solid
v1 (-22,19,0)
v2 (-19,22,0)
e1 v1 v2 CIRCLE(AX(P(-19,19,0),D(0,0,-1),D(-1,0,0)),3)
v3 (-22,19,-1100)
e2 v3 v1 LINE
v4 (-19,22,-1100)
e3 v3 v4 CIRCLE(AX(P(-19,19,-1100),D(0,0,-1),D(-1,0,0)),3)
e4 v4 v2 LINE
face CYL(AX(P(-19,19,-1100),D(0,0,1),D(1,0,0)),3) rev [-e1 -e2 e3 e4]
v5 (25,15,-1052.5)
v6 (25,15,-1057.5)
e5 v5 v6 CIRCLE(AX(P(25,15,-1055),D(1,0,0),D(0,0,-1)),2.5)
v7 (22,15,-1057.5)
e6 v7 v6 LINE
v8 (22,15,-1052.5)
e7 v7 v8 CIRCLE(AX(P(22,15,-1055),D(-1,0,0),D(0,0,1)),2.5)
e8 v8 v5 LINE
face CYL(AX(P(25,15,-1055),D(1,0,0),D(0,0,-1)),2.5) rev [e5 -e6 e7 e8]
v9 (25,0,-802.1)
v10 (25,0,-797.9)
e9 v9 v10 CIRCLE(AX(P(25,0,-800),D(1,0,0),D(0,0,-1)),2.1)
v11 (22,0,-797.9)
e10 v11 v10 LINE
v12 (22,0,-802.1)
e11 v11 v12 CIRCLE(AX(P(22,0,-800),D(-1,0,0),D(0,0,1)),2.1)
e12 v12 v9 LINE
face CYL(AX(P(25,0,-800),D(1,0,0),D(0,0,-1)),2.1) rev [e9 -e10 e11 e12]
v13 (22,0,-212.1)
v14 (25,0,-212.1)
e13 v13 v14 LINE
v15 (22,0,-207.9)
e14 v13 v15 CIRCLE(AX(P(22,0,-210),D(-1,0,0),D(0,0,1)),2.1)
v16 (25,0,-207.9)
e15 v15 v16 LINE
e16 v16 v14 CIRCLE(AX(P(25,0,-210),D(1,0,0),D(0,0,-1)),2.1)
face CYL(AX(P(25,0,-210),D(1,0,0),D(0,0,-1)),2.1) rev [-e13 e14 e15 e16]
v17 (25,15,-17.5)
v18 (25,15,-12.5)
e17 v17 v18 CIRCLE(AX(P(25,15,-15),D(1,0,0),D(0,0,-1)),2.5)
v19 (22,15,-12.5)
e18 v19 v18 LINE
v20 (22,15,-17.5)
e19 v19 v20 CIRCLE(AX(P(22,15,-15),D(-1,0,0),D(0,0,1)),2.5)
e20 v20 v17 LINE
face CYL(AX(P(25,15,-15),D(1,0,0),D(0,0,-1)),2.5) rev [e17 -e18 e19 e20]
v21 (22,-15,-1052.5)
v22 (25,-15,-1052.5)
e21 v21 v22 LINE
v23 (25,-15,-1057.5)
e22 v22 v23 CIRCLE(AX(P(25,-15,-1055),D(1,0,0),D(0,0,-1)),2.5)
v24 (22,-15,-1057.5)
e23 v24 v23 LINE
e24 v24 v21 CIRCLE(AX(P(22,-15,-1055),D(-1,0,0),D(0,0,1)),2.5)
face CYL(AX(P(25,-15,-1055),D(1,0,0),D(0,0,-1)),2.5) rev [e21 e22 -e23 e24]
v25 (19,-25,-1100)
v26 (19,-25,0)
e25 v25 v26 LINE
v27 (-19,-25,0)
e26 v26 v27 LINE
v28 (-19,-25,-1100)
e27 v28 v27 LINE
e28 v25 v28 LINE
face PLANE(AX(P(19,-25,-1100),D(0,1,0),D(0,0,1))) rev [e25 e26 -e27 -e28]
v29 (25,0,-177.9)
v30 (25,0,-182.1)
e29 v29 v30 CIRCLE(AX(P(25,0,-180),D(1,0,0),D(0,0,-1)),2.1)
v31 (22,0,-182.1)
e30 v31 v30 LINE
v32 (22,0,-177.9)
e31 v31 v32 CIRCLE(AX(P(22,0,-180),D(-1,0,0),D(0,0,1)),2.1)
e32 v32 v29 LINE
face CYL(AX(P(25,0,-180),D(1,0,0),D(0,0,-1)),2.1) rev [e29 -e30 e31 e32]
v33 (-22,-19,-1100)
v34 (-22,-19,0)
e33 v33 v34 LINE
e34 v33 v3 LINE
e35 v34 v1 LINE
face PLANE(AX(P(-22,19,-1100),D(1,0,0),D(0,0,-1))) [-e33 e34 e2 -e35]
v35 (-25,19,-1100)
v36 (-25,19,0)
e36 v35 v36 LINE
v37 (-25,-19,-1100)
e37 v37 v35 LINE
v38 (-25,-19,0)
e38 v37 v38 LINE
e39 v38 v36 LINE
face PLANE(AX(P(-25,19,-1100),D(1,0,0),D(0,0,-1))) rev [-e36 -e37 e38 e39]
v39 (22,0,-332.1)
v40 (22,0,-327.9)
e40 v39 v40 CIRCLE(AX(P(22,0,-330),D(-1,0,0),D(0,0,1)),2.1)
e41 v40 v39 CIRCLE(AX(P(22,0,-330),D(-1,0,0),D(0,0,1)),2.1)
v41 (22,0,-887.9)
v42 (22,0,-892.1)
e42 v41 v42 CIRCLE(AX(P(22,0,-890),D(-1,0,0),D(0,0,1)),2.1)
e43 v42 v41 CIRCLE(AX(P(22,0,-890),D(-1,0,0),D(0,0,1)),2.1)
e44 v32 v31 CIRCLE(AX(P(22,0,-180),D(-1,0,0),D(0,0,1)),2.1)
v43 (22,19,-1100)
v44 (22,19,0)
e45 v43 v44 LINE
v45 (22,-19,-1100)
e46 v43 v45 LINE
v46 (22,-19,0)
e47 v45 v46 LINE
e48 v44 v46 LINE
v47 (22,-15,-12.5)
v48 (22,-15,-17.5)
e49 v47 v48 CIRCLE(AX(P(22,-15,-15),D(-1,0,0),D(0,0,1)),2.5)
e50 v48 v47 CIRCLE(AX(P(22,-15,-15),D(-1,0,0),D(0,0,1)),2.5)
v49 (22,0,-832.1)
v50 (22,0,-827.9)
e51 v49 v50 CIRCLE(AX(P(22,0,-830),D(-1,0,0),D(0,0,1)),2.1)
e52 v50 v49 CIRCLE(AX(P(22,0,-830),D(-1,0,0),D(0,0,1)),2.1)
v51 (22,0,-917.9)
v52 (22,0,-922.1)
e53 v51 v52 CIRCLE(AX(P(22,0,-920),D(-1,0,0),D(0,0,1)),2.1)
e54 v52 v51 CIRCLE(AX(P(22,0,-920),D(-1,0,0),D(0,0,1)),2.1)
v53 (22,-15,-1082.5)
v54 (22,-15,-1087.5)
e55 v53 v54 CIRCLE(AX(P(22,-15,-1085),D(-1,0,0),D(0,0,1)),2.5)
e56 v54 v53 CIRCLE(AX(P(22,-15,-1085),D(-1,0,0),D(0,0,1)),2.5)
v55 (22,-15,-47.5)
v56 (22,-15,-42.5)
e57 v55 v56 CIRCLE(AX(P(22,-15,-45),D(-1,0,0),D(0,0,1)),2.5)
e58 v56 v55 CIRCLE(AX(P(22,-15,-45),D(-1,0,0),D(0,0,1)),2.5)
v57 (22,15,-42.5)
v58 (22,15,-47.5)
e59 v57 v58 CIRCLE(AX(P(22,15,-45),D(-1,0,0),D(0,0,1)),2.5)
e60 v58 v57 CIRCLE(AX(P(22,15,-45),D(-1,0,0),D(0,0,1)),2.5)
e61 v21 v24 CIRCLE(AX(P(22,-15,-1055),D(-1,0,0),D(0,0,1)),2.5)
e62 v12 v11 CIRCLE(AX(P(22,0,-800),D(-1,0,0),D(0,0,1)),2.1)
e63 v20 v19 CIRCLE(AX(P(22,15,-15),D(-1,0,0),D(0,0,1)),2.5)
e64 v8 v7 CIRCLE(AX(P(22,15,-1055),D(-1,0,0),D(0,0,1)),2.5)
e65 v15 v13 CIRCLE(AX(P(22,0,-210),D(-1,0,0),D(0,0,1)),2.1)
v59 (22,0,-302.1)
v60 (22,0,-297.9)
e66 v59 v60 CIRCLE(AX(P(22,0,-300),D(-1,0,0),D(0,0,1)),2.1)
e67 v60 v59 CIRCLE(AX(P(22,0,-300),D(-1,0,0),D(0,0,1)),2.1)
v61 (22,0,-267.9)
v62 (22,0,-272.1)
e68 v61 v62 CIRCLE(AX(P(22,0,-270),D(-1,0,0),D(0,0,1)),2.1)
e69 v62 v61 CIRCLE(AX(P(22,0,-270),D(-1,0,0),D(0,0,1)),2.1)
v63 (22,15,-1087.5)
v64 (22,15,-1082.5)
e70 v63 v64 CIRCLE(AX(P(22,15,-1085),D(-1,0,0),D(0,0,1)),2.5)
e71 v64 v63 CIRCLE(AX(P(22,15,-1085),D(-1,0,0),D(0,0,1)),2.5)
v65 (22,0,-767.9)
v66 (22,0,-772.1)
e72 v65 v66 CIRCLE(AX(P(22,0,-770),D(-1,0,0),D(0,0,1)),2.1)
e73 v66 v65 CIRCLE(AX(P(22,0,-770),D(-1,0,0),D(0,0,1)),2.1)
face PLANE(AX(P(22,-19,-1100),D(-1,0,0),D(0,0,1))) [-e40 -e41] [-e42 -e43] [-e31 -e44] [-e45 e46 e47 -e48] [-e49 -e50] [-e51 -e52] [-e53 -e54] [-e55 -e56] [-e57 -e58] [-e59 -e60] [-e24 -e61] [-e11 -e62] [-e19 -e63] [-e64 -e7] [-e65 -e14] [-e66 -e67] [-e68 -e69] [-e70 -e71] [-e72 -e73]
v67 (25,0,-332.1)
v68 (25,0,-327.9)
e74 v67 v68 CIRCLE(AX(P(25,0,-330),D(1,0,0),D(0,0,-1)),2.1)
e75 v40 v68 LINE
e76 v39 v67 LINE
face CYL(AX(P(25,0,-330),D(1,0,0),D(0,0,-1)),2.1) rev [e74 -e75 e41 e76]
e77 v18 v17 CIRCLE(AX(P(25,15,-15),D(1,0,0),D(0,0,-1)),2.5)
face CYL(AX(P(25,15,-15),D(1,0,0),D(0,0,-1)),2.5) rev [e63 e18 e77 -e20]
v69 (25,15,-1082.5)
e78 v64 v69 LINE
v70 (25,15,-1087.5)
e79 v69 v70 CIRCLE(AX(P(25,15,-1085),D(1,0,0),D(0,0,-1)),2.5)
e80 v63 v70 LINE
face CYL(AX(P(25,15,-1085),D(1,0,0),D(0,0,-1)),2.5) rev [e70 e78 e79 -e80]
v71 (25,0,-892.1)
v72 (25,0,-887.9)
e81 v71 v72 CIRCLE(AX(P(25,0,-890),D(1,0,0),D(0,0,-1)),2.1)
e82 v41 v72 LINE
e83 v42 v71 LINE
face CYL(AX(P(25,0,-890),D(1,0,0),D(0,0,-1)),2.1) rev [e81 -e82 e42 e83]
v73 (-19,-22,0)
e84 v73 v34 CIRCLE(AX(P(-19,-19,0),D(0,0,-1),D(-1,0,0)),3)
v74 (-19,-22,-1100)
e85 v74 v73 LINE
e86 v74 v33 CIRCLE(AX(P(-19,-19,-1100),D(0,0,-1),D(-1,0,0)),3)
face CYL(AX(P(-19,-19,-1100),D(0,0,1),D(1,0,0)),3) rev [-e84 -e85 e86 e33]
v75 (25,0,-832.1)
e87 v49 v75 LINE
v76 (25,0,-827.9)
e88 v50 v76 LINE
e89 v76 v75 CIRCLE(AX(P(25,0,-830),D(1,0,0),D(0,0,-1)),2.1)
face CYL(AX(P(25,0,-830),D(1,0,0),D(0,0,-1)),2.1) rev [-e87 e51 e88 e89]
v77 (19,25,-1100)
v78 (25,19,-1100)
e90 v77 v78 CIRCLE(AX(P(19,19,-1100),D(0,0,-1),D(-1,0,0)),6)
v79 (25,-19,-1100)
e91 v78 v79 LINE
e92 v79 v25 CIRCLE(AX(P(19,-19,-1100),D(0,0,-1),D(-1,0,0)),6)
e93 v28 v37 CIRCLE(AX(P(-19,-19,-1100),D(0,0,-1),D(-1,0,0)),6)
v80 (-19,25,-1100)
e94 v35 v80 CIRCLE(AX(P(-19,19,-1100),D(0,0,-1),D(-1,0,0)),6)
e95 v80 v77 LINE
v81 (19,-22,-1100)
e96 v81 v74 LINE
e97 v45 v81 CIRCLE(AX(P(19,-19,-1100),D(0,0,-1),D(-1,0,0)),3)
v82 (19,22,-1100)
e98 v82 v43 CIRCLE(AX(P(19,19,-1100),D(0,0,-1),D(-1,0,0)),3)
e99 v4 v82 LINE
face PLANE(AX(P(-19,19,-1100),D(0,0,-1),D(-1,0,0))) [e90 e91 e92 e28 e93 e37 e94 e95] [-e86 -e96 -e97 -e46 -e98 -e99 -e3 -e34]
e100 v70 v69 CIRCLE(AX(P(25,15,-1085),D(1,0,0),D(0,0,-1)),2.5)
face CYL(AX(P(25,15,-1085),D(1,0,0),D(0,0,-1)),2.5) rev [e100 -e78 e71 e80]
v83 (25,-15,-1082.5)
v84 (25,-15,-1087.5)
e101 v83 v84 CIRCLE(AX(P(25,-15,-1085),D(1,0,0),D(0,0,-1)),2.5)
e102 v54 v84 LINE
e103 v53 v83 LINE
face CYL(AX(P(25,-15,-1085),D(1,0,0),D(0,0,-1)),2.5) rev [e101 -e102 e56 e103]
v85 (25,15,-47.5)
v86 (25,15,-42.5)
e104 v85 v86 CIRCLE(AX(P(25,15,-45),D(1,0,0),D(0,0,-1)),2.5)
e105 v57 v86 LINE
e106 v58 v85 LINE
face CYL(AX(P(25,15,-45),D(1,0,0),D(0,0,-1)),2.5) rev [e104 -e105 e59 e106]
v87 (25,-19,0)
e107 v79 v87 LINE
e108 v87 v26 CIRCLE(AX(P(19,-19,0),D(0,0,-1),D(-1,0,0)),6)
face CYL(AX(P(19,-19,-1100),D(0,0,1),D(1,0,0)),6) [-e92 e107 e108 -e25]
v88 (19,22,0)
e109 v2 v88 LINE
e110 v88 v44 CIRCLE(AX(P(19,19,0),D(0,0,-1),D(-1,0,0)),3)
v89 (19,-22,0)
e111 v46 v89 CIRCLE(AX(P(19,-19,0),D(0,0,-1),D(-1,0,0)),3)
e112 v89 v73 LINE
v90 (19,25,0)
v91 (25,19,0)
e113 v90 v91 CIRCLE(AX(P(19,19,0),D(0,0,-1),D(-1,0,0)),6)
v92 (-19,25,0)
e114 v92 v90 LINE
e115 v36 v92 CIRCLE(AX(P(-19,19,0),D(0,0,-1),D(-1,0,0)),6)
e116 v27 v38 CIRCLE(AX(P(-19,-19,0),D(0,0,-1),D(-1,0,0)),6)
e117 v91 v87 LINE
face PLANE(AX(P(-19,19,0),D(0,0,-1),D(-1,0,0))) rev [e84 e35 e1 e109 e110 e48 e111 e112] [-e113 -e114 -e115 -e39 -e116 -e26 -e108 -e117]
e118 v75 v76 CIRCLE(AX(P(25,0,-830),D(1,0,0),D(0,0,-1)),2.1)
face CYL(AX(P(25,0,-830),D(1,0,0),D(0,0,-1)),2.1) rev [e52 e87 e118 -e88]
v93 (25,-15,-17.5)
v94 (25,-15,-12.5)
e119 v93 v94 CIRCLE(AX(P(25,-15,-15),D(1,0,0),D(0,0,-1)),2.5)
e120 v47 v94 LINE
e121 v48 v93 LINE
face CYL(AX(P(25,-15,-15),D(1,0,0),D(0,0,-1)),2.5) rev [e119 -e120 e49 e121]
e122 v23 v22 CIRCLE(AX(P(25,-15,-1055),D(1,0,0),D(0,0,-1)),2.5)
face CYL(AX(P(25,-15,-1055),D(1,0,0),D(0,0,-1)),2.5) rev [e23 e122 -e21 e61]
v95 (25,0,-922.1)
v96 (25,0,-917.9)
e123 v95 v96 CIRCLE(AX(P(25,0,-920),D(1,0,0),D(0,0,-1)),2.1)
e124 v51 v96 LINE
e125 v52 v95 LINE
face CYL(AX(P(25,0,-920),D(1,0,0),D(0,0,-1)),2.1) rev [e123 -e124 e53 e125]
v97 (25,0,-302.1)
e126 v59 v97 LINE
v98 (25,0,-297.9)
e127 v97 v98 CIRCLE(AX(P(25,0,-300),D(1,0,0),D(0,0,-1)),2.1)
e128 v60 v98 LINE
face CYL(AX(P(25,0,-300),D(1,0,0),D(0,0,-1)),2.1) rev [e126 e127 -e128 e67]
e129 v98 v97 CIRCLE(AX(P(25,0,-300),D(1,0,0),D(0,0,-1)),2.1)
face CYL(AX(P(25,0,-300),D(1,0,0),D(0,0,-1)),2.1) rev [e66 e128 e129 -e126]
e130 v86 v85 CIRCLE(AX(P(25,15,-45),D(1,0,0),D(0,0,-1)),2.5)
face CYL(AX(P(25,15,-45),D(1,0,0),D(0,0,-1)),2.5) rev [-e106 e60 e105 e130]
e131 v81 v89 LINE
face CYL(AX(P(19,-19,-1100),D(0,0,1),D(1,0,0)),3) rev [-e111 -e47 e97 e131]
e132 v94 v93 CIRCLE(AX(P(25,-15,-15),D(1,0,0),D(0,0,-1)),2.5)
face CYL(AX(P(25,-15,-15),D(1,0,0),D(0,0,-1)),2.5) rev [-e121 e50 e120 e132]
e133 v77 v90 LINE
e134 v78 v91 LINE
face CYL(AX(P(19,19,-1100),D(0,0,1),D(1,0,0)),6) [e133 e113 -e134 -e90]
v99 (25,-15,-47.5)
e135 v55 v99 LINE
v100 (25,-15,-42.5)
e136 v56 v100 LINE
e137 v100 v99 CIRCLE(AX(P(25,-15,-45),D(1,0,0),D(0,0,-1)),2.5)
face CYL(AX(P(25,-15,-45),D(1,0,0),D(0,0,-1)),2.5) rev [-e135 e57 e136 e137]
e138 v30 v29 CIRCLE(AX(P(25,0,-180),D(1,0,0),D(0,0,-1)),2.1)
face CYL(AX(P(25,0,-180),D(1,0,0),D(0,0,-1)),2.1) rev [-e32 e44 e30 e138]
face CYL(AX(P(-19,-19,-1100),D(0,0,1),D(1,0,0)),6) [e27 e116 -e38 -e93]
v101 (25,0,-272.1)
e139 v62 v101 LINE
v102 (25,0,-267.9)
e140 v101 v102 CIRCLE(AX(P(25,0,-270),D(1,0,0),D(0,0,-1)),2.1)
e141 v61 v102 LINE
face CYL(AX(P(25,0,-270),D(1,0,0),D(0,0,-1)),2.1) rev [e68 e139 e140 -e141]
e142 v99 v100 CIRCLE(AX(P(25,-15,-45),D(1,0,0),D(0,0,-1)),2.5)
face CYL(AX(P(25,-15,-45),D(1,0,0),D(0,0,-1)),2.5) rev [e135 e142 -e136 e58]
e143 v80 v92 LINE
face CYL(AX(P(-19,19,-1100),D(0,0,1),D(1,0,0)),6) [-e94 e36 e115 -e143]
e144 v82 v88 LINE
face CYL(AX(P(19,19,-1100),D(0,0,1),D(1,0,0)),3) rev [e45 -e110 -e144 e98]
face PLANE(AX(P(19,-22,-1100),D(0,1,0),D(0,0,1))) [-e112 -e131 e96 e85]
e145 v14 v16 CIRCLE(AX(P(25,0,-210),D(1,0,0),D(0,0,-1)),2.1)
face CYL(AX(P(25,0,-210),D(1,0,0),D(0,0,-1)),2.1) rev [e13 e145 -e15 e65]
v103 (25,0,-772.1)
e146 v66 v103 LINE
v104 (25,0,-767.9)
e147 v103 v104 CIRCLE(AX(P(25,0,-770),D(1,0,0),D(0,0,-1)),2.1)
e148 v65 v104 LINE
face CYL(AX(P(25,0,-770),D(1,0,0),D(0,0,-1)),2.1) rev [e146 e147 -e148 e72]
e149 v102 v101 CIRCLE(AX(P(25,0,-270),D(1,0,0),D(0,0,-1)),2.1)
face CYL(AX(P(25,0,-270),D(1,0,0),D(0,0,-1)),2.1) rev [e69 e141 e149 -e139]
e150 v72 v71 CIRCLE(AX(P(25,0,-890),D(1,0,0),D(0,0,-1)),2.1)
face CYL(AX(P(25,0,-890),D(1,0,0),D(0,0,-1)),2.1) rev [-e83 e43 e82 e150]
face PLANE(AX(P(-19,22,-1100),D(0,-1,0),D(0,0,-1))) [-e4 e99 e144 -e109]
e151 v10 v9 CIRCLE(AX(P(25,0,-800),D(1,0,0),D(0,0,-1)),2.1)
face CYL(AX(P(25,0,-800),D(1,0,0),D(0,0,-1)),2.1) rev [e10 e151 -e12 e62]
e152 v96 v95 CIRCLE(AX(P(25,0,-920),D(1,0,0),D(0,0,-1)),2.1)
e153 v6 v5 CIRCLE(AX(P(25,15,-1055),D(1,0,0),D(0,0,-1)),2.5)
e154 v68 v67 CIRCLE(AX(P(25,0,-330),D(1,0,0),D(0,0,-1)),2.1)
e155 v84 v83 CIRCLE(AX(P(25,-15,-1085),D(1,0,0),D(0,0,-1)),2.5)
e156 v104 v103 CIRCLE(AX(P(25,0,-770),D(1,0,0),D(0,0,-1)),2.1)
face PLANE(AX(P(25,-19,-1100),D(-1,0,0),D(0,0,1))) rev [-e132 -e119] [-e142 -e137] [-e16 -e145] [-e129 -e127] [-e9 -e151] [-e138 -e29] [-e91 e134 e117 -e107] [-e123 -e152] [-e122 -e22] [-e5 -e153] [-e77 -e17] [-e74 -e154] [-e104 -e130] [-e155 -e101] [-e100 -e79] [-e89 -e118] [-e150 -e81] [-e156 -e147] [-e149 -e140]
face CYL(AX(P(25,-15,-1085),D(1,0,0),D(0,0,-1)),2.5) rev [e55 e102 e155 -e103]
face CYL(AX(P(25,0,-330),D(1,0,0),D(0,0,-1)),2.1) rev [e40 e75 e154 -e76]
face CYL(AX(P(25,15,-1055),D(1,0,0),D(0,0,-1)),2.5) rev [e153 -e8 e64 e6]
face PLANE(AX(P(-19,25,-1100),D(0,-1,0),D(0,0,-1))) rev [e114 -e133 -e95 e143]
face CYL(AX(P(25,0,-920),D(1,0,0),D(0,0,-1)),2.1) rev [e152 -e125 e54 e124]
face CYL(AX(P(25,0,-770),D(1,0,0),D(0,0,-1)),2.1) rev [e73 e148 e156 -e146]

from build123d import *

# Parameters (mm, degrees)
GB_6728_1986_050_X_50_X_3_1_DEPTH = 1100
HOLE_WIZARD_M5_1_D                = 4.2
HOLE_WIZARD_M5_1_DEPTH            = 12.4
HOLE_WIZARD_M5_1_TIP              = 1.2618073
HOLE_WIZARD_M5_2_D                = 4.2
HOLE_WIZARD_M5_2_DEPTH            = 15
HOLE_WIZARD_M5_2_TIP              = 1.2618073
HOLE_WIZARD_M5_3_D                = 4.2
HOLE_WIZARD_M5_3_DEPTH            = 12.4
HOLE_WIZARD_M5_3_TIP              = 1.2618073
HOLE_WIZARD_M6_1_D                = 5
HOLE_WIZARD_M6_1_DEPTH            = 15
HOLE_WIZARD_M6_1_TIP              = 1.502151548


with BuildPart() as part:
    # Sketch1 → Gb／6728-1986方形空心型钢 050 X 50 X 3(1) (new body)
    with BuildSketch(Plane(origin=(0, 0, 0), x_dir=(-1, 0, 0), z_dir=(0, 0, -1))):
        with BuildLine():
            Line((-19, -25), (19, -25))
            ThreePointArc((19, -25), (23.242640687, -23.242640687), (25, -19))
            Line((25, -19), (25, 19))
            ThreePointArc((25, 19), (23.242640687, 23.242640687), (19, 25))
            Line((19, 25), (-19, 25))
            ThreePointArc((-19, 25), (-23.242640687, 23.242640687), (-25, 19))
            Line((-25, 19), (-25, -19))
            ThreePointArc((-25, -19), (-23.242640687, -23.242640687), (-19, -25))
        make_face()
        with BuildLine():
            Line((-19, -22), (19, -22))
            ThreePointArc((19, -22), (21.121320344, -21.121320344), (22, -19))
            Line((22, -19), (22, 19))
            ThreePointArc((22, 19), (21.121320344, 21.121320344), (19, 22))
            Line((19, 22), (-19, 22))
            ThreePointArc((-19, 22), (-21.121320344, 21.121320344), (-22, 19))
            Line((-22, 19), (-22, -19))
            ThreePointArc((-22, -19), (-21.121320344, -21.121320344), (-19, -22))
        make_face(mode=Mode.SUBTRACT)
    extrude(amount=GB_6728_1986_050_X_50_X_3_1_DEPTH)

    # M5 螺纹孔1
    with Locations(Plane(origin=(25, 0, 0), x_dir=(0, 0, -1), z_dir=(1, 0, 0))):
        with Locations((180, 0), (210, 0)):
            Hole(HOLE_WIZARD_M5_1_D / 2, depth=HOLE_WIZARD_M5_1_DEPTH)
            with Locations((0, 0, -(HOLE_WIZARD_M5_1_DEPTH + HOLE_WIZARD_M5_1_TIP / 2))):  # 118° drill point
                Cone(0, HOLE_WIZARD_M5_1_D / 2, HOLE_WIZARD_M5_1_TIP, mode=Mode.SUBTRACT)

    # M5 螺纹孔2
    with Locations(Plane(origin=(25, 0, 0), x_dir=(0, 0, -1), z_dir=(1, 0, 0))):
        with Locations((270, 0), (300, 0), (330, 0)):
            Hole(HOLE_WIZARD_M5_2_D / 2, depth=HOLE_WIZARD_M5_2_DEPTH)
            with Locations((0, 0, -(HOLE_WIZARD_M5_2_DEPTH + HOLE_WIZARD_M5_2_TIP / 2))):  # 118° drill point
                Cone(0, HOLE_WIZARD_M5_2_D / 2, HOLE_WIZARD_M5_2_TIP, mode=Mode.SUBTRACT)

    # M5 螺纹孔3
    with Locations(Plane(origin=(25, 0, 0), x_dir=(0, 0, -1), z_dir=(1, 0, 0))):
        with Locations((920, 0), (890, 0), (830, 0), (800, 0), (770, 0)):
            Hole(HOLE_WIZARD_M5_3_D / 2, depth=HOLE_WIZARD_M5_3_DEPTH)
            with Locations((0, 0, -(HOLE_WIZARD_M5_3_DEPTH + HOLE_WIZARD_M5_3_TIP / 2))):  # 118° drill point
                Cone(0, HOLE_WIZARD_M5_3_D / 2, HOLE_WIZARD_M5_3_TIP, mode=Mode.SUBTRACT)

    # M6 螺纹孔1
    with Locations(Plane(origin=(25, 0, 0), x_dir=(0, 0, -1), z_dir=(1, 0, 0))):
        with Locations((15, 15), (45, 15), (15, -15), (45, -15), (1055, 15), (1085, 15), (1055, -15), (1085, -15)):
            Hole(HOLE_WIZARD_M6_1_D / 2, depth=HOLE_WIZARD_M6_1_DEPTH)
            with Locations((0, 0, -(HOLE_WIZARD_M6_1_DEPTH + HOLE_WIZARD_M6_1_TIP / 2))):  # 118° drill point
                Cone(0, HOLE_WIZARD_M6_1_D / 2, HOLE_WIZARD_M6_1_TIP, mode=Mode.SUBTRACT)


solid = part.part
